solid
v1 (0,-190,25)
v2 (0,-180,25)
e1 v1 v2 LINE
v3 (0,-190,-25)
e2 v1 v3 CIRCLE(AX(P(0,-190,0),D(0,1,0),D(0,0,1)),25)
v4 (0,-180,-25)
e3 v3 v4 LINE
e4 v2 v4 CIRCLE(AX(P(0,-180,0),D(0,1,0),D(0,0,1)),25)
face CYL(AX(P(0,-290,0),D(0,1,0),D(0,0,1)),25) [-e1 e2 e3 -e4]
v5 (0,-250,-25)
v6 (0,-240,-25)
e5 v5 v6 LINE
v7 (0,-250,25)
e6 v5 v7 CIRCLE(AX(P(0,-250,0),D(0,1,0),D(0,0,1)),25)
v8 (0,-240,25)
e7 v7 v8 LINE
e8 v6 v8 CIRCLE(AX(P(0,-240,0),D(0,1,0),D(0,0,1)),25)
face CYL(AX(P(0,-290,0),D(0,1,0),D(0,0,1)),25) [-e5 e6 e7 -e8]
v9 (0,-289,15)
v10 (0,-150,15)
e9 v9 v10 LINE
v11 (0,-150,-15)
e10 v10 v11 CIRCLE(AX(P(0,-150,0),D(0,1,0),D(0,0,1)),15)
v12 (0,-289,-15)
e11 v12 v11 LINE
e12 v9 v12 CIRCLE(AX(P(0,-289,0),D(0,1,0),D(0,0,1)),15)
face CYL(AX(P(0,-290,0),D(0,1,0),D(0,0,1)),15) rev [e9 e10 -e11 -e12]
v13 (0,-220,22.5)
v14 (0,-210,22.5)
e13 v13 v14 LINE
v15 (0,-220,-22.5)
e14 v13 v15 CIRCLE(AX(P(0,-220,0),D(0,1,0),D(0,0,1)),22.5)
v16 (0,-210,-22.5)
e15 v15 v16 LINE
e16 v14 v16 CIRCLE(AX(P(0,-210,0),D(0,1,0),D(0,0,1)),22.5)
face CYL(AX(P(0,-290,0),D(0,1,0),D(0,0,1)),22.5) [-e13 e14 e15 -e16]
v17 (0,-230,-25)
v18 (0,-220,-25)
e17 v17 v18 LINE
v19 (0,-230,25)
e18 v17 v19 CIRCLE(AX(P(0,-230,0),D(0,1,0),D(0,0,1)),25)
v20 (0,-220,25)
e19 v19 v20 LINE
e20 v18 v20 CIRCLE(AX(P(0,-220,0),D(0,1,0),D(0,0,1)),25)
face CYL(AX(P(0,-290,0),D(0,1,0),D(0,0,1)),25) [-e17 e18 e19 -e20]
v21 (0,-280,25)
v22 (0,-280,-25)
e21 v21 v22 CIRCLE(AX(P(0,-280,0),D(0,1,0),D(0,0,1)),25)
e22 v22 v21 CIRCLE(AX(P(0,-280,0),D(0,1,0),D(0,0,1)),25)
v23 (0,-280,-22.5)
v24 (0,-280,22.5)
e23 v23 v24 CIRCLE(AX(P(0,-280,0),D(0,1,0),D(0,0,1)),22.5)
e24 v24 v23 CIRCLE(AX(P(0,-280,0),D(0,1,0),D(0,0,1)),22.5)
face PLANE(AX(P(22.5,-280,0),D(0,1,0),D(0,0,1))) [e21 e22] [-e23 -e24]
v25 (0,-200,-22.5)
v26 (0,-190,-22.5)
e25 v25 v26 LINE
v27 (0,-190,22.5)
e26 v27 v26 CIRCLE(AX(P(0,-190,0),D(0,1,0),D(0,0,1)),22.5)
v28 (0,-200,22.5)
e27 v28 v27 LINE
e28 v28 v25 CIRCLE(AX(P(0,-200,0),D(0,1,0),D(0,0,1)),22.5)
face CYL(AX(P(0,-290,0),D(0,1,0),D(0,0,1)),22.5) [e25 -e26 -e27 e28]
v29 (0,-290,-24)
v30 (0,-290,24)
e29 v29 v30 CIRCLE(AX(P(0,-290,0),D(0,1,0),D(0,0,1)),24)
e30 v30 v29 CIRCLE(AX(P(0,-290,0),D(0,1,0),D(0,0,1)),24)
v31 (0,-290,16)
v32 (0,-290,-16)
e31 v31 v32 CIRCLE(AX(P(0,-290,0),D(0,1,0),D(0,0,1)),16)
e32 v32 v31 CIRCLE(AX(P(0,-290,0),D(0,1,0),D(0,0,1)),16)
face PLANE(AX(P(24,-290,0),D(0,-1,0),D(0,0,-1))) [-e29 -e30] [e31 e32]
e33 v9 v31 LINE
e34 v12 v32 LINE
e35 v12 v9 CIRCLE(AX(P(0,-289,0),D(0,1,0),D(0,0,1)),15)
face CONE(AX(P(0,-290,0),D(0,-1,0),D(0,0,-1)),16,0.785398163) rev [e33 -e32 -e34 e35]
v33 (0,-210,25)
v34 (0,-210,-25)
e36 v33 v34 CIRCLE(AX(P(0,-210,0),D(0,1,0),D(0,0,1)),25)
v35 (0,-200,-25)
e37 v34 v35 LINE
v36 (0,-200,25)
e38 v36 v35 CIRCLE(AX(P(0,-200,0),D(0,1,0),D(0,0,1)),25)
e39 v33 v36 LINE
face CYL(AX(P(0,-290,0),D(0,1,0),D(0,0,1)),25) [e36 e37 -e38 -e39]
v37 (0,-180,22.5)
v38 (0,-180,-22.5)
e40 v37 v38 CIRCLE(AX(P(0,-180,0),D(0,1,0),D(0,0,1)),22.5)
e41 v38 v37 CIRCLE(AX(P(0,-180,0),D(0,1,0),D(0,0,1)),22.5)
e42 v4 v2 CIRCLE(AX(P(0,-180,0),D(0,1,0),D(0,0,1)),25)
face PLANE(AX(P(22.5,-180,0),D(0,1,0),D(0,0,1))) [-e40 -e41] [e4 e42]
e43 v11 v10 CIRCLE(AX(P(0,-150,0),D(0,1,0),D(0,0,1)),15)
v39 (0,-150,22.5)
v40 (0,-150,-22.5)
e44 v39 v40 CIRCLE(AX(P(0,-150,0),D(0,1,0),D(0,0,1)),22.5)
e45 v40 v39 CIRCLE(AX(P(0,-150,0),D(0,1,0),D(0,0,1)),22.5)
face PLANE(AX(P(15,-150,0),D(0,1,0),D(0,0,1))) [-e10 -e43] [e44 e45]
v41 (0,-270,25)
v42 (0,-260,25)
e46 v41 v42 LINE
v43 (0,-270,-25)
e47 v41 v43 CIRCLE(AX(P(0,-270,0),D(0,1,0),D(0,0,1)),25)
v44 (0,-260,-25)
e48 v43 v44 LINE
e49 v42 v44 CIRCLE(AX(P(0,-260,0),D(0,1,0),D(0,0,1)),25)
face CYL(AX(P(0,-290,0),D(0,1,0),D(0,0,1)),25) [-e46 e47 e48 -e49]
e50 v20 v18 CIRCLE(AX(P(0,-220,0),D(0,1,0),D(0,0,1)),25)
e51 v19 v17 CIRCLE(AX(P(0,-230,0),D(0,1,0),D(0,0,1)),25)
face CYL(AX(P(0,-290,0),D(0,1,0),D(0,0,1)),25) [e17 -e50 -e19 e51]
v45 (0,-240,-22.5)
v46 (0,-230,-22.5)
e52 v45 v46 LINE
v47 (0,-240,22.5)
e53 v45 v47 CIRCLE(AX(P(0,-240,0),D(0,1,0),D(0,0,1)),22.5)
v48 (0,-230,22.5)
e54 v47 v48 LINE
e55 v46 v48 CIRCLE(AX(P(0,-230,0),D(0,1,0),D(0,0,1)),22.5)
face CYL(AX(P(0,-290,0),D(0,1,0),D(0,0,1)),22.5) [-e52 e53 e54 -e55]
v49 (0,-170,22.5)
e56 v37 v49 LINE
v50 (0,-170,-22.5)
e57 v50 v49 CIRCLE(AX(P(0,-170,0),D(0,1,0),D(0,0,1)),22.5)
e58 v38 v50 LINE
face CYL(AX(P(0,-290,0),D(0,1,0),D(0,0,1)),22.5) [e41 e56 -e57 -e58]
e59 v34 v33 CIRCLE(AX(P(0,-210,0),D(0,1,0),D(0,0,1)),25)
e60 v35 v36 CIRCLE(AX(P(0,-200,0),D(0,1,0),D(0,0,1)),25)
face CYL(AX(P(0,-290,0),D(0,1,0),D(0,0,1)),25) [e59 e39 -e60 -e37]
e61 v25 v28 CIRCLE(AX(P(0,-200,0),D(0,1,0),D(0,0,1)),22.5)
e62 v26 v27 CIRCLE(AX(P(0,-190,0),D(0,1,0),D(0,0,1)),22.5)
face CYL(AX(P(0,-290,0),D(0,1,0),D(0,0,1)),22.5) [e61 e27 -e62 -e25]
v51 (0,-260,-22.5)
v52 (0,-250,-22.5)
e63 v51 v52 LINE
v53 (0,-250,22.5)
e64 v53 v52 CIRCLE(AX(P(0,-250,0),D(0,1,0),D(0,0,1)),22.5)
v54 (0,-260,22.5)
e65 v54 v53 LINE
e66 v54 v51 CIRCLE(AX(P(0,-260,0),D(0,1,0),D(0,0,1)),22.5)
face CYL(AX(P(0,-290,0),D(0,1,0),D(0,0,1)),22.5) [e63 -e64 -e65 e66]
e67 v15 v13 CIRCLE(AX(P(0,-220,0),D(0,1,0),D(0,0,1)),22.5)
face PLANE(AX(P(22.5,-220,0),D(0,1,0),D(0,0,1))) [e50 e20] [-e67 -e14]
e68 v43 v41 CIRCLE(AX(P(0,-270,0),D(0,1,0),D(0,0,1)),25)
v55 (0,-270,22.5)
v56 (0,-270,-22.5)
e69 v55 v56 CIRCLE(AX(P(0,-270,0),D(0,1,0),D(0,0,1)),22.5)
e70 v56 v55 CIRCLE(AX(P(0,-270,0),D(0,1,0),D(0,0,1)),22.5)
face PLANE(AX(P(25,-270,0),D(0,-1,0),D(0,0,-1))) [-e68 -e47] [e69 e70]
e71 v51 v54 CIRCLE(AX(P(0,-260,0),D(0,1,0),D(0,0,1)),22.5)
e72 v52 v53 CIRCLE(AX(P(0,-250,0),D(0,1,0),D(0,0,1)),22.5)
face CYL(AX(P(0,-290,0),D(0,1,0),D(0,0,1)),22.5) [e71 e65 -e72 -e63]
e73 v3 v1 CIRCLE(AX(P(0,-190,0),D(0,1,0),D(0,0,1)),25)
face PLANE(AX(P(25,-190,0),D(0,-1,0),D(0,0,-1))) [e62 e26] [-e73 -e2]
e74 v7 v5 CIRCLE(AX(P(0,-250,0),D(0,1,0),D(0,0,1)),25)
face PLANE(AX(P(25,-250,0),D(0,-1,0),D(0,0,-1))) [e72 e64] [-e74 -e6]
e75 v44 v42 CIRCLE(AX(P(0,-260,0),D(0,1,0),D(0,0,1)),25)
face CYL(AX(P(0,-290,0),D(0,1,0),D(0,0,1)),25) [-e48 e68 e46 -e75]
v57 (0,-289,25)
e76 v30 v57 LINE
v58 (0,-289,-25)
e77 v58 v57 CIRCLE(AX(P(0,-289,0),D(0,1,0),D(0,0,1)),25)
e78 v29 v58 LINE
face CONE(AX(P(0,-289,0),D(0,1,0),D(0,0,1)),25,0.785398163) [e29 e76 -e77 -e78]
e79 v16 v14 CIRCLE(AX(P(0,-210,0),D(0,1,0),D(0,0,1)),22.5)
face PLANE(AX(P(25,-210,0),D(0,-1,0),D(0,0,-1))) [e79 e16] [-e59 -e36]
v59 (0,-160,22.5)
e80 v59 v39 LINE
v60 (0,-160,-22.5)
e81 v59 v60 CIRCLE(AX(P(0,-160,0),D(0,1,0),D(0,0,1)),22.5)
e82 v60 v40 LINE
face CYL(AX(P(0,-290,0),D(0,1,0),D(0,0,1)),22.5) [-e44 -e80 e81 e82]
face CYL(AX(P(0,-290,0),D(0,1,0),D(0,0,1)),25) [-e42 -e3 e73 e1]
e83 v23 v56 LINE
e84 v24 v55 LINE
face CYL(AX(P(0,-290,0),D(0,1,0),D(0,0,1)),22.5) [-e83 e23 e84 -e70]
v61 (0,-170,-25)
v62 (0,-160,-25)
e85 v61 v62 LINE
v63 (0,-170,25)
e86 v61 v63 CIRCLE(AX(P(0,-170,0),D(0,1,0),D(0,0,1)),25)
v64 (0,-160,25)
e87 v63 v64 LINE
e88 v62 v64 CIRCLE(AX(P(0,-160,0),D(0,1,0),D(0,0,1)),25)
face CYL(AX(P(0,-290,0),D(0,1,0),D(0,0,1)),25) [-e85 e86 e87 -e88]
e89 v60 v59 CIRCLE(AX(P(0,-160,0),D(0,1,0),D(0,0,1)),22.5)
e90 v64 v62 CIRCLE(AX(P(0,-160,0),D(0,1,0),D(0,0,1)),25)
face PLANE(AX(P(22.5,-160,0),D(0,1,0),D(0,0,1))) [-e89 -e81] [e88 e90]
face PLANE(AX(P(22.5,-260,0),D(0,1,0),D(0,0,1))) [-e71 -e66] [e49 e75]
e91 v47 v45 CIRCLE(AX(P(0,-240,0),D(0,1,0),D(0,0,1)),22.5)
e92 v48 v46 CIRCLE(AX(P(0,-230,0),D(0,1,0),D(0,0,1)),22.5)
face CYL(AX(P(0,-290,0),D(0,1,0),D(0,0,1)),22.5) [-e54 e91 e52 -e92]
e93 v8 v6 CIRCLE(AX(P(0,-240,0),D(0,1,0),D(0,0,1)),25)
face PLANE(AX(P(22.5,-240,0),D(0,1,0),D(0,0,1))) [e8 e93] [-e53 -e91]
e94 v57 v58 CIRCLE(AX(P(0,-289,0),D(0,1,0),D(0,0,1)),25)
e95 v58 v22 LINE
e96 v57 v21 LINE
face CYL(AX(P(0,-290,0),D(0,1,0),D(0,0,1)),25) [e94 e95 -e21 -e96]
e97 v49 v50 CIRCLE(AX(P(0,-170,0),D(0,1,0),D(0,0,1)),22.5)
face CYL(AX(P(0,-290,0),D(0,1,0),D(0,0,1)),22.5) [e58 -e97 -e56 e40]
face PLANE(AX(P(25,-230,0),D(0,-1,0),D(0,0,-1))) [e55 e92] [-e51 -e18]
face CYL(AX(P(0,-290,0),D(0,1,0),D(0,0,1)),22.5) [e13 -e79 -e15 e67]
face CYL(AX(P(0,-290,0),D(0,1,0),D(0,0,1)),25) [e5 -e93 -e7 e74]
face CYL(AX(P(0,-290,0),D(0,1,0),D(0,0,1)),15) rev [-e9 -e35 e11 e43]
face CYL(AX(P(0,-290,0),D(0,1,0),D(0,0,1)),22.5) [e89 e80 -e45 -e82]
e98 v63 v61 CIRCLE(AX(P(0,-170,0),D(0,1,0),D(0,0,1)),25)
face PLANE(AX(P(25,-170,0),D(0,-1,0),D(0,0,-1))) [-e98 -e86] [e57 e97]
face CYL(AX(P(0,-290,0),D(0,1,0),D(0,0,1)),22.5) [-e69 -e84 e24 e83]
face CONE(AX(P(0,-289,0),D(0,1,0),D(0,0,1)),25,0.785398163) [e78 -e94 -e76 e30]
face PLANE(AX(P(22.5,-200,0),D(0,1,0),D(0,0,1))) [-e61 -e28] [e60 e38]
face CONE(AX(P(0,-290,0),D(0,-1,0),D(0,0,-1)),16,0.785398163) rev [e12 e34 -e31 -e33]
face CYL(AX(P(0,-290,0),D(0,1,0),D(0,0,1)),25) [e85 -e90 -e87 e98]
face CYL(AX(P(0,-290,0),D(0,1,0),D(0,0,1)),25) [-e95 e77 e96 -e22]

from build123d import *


with BuildPart() as part:
    # 草图1 → 旋转1 (revolve)
    with BuildSketch(Plane(origin=(0, 0, 0), x_dir=(-1, 0, 0), z_dir=(0, 0, -1)), mode=Mode.PRIVATE) as revolve_1_sk:
        Polygon((-22.5, -220), (-25, -220), (-25, -230), (-22.5, -230), (-22.5, -240), (-25, -240), (-25, -250), (-22.5, -250), (-22.5, -260), (-25, -260), (-25, -270), (-22.5, -270), (-22.5, -280), (-25, -280), (-25, -289), (-24, -290), (-16, -290), (-15, -289), (-15, -150), (-22.5, -150), (-22.5, -160), (-25, -160), (-25, -170), (-22.5, -170), (-22.5, -180), (-25, -180), (-25, -190), (-22.5, -190), (-22.5, -200), (-25, -200), (-25, -210), (-22.5, -210), align=None)
    revolve(revolve_1_sk.sketch.rotate(Axis((0, -290, 0), (0, 1, 0)), 270), axis=Axis((0, -290, 0), (0, 1, 0)))


solid = part.part
